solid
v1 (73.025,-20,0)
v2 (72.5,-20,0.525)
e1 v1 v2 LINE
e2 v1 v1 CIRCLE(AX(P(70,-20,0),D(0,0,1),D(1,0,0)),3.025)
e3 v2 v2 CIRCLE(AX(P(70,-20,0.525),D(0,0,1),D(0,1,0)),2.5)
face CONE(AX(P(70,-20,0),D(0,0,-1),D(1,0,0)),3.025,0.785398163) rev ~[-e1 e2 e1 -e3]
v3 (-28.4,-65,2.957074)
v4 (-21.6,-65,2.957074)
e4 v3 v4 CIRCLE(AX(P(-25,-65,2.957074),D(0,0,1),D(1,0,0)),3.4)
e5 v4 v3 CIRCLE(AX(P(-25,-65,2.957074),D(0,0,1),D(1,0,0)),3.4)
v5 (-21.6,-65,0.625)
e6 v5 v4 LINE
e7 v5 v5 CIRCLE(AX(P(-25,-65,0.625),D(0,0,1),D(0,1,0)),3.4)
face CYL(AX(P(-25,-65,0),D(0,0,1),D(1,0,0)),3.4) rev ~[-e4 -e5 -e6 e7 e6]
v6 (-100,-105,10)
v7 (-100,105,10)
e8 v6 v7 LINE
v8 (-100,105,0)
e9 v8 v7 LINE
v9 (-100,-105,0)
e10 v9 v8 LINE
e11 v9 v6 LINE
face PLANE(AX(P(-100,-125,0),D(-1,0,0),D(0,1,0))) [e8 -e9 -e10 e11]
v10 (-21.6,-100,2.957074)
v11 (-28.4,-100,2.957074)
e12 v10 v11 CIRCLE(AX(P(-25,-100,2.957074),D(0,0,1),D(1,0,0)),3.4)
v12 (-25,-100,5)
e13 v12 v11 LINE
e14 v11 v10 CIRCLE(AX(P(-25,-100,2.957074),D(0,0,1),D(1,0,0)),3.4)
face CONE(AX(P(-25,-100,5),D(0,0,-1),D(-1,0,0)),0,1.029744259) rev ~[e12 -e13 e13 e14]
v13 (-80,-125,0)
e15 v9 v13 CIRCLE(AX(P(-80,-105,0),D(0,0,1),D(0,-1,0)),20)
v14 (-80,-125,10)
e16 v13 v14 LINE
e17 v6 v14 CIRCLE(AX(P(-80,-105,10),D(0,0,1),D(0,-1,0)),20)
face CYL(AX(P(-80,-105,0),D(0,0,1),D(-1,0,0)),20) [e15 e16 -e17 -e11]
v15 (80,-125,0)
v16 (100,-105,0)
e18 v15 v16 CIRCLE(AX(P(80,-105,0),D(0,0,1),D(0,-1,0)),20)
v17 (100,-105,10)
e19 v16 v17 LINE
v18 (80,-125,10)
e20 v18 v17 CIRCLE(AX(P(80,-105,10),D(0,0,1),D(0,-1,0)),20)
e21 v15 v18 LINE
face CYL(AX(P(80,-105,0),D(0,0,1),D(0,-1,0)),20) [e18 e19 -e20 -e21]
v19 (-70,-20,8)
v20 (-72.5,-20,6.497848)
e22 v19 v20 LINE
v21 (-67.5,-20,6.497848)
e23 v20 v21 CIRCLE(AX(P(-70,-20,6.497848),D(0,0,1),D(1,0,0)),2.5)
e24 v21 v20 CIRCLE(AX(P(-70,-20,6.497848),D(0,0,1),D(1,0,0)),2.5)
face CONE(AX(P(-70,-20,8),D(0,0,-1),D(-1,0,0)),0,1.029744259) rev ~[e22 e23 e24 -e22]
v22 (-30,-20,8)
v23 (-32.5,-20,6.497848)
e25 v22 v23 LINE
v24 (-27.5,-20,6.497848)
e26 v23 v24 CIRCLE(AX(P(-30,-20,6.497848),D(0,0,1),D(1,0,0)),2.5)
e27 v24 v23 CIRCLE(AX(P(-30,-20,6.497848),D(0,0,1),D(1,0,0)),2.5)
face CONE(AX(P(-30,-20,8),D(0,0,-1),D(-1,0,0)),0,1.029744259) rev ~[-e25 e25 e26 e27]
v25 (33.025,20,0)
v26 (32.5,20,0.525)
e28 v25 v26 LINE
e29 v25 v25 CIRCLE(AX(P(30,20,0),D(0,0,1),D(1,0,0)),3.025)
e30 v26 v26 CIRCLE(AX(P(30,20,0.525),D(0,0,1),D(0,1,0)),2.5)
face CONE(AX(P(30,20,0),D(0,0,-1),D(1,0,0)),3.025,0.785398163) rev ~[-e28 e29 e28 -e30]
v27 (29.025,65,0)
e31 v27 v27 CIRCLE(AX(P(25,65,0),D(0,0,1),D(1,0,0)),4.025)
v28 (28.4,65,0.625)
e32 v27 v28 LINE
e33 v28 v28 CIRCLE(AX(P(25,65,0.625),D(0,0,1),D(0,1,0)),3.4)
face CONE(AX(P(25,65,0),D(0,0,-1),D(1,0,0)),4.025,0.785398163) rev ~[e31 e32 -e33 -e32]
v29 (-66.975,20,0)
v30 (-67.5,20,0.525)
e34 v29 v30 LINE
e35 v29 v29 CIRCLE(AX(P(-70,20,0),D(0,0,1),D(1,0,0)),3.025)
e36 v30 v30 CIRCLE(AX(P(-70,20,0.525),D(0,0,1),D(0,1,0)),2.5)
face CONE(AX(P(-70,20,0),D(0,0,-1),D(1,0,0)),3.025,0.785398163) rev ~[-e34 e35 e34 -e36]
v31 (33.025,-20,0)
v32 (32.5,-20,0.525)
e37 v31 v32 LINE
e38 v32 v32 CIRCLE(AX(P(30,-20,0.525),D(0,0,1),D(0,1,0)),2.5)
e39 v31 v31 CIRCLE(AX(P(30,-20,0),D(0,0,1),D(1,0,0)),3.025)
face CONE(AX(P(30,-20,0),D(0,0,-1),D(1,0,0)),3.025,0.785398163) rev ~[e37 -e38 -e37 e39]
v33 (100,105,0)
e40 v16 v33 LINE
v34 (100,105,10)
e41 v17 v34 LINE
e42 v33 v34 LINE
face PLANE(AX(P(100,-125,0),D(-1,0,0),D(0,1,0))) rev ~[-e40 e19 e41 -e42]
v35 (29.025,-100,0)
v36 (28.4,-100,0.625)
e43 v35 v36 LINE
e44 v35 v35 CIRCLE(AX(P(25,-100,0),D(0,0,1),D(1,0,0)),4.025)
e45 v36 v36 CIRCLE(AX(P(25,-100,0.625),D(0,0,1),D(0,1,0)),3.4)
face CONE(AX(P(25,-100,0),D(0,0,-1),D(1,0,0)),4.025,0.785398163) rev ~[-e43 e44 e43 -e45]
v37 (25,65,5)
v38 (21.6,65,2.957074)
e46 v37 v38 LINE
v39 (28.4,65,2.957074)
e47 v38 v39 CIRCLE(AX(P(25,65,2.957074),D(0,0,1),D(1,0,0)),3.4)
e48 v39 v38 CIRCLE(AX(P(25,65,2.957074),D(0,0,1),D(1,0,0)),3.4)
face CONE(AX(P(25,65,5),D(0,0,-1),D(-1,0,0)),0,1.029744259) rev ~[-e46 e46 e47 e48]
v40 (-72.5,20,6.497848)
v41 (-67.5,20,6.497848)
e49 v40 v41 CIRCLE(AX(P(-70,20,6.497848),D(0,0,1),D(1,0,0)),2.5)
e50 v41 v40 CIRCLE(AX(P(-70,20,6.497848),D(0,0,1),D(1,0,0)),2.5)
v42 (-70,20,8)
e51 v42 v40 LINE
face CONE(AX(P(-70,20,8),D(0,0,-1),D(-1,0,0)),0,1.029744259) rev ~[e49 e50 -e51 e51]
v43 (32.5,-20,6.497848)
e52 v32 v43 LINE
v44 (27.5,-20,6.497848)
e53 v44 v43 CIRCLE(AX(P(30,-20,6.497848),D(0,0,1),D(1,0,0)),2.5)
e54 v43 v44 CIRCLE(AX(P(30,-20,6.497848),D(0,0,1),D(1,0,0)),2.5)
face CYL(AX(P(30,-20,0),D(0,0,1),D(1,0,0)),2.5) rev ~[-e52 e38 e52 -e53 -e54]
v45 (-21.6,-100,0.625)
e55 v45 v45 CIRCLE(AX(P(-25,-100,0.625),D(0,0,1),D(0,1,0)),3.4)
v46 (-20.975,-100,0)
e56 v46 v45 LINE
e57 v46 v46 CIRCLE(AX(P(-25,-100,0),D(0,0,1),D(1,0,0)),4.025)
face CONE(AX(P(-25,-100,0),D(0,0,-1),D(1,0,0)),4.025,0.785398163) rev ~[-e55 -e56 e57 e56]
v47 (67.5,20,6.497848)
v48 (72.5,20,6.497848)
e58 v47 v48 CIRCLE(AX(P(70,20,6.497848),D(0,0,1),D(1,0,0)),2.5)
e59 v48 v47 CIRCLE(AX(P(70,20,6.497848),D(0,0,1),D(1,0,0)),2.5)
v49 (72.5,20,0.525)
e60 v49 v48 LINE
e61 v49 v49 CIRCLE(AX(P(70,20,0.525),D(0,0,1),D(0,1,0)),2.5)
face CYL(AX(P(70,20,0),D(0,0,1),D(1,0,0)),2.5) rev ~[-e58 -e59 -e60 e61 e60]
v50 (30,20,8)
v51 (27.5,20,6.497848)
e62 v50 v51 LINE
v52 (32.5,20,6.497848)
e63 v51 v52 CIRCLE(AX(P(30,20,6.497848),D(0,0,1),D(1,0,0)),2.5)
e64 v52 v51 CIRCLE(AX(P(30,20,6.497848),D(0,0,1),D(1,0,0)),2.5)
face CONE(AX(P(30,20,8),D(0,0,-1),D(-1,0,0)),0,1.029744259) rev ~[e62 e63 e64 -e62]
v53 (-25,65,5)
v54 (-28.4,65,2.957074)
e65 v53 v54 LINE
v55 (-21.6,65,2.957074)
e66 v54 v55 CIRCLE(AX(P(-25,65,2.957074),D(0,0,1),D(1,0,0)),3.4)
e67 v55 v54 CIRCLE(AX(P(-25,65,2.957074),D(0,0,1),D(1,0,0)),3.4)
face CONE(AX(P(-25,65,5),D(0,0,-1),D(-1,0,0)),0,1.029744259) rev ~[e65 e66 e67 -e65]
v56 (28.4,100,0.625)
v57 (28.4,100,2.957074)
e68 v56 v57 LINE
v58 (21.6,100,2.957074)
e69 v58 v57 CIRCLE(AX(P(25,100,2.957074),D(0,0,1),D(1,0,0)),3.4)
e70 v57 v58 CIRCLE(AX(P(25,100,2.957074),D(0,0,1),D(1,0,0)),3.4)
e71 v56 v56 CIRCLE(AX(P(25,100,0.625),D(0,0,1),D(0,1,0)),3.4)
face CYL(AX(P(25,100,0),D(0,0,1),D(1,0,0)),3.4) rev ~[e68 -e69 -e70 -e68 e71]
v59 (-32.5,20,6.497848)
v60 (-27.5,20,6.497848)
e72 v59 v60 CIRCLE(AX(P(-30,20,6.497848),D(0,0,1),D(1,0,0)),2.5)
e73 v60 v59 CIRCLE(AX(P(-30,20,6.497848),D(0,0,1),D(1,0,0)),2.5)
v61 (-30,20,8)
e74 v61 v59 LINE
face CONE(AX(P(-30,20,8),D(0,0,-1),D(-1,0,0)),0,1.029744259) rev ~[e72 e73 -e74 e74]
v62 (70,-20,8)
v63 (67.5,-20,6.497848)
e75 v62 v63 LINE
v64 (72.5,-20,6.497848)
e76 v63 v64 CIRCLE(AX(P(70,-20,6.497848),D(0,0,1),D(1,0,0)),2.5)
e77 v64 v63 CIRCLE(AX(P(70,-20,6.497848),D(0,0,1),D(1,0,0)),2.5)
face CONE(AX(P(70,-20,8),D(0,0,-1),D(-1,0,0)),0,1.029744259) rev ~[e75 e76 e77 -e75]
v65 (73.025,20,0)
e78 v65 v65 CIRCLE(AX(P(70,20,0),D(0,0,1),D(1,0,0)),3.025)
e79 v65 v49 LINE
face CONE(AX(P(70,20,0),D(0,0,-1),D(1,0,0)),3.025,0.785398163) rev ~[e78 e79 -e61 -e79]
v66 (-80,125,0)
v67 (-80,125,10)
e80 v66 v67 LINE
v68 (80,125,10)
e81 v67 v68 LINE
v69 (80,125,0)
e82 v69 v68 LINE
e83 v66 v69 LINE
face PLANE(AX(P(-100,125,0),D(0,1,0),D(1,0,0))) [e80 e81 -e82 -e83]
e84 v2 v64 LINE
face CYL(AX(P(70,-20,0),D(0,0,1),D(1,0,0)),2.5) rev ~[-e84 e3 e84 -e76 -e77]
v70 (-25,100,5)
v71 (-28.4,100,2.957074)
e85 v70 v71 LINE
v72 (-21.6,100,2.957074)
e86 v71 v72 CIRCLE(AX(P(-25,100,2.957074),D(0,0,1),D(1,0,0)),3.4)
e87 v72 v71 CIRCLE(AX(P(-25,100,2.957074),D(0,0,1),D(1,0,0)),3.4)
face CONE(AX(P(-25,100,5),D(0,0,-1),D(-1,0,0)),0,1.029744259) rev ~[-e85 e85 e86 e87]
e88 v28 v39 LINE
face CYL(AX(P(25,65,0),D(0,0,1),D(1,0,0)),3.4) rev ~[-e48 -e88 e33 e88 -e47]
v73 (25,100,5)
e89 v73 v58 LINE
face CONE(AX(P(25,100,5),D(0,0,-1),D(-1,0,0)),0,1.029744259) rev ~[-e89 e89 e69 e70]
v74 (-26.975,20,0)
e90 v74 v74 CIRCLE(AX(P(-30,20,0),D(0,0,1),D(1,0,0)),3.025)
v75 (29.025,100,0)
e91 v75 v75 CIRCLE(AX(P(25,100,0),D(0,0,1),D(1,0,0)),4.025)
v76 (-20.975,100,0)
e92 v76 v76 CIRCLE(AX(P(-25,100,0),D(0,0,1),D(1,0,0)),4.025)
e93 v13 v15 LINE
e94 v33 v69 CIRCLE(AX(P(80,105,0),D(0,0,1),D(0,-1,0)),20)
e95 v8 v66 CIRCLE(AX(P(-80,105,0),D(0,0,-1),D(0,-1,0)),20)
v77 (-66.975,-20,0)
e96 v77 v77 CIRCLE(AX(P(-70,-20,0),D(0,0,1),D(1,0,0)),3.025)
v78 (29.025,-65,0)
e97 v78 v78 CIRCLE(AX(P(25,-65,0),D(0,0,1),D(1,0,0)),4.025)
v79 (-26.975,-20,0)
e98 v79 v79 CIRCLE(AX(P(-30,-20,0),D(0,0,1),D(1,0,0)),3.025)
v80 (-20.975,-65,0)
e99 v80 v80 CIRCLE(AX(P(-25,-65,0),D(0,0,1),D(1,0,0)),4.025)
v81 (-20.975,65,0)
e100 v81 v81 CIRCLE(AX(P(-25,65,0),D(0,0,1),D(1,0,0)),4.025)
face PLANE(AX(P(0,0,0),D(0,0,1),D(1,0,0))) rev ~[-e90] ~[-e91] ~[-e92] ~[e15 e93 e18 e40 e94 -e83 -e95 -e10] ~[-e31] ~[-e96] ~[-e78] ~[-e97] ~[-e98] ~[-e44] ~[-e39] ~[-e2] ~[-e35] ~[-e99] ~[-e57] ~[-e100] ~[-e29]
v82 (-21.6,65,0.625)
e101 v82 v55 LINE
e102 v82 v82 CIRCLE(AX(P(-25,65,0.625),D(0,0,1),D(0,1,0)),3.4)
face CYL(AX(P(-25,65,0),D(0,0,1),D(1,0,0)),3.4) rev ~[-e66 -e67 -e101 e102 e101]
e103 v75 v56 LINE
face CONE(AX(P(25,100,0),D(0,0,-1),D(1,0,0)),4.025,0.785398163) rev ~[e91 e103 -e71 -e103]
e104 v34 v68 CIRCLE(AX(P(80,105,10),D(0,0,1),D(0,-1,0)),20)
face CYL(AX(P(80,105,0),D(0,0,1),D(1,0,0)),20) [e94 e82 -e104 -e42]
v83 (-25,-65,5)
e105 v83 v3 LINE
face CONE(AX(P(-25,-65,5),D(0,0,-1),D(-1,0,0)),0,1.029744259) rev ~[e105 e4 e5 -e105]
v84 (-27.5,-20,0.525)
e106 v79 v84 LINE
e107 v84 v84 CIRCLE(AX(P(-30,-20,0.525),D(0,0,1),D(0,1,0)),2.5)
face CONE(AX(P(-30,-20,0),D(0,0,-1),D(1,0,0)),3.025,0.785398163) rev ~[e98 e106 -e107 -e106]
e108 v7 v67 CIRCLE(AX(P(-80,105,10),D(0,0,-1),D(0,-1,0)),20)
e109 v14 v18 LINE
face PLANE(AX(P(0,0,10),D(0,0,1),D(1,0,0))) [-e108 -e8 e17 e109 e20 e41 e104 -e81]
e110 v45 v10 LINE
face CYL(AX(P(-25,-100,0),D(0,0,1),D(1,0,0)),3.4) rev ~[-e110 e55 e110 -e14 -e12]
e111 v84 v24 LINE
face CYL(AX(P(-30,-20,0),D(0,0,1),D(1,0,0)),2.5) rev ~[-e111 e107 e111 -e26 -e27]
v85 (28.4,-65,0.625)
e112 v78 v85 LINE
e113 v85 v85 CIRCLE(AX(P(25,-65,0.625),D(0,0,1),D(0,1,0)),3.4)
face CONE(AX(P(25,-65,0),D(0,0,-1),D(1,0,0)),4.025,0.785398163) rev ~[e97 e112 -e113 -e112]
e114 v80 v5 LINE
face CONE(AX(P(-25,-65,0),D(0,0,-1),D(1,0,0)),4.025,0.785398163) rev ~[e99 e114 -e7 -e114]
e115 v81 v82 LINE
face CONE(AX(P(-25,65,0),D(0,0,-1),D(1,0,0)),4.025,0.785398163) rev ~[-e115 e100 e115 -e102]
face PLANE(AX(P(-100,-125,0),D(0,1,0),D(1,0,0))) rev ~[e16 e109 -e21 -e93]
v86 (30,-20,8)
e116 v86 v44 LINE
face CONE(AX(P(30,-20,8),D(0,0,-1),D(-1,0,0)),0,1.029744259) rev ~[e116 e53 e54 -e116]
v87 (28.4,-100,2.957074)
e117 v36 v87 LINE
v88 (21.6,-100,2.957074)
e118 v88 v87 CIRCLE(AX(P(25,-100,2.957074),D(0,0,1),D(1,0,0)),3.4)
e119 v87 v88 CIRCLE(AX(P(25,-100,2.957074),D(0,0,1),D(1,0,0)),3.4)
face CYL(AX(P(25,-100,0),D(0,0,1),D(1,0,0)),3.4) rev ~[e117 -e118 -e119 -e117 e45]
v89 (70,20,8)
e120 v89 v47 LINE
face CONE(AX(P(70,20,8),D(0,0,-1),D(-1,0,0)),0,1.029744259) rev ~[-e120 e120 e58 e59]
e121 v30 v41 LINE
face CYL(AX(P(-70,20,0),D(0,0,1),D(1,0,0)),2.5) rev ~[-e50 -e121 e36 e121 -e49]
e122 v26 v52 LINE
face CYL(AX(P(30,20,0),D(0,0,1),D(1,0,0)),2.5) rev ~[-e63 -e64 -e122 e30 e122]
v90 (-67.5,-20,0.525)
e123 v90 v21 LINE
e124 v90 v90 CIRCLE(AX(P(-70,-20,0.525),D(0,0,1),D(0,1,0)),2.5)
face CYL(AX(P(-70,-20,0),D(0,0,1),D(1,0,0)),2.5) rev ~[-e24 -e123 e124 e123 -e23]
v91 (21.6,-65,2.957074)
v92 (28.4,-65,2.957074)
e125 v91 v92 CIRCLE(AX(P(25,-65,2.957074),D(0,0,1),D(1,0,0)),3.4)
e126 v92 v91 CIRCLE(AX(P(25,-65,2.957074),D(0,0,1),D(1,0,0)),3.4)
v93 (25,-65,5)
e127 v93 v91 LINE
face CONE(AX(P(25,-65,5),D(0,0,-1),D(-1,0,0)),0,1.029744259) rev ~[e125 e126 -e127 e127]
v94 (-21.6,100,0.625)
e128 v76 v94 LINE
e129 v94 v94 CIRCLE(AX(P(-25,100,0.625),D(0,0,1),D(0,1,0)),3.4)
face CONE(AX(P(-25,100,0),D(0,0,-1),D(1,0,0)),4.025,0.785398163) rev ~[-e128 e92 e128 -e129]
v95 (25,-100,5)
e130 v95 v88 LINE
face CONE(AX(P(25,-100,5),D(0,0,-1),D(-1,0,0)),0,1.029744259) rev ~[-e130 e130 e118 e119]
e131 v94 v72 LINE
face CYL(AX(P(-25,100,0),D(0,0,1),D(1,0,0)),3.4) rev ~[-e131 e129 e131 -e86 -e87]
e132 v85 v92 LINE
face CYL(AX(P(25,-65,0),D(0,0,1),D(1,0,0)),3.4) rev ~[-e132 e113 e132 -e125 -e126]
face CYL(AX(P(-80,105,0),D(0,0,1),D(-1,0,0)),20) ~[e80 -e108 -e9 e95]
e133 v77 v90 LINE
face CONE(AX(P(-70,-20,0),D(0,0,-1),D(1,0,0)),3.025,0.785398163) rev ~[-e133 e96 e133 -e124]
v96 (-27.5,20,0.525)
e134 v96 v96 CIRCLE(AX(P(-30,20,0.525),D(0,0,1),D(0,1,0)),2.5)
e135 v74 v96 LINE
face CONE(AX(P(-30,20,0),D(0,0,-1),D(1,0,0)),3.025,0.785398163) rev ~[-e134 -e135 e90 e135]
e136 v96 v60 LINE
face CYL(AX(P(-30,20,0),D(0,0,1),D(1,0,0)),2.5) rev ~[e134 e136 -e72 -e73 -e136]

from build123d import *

# Parameters (mm, degrees)
SKETCH_1_W                   = 200
SKETCH_1_H                   = 250
EXTRUDE_1_DEPTH              = 10
FILLET_1_R                   = 20
HOLE_WIZARD_M8_2_D           = 6.8
HOLE_WIZARD_M8_2_DEPTH       = 2.957073895
HOLE_WIZARD_M8_2_CSINK_D     = 8.05
HOLE_WIZARD_M8_2_CSINK_ANGLE = 90
HOLE_WIZARD_M8_2_TIP         = 2.042926105
HOLE_WIZARD_M6_1_D           = 5
HOLE_WIZARD_M6_1_DEPTH       = 6.497848452
HOLE_WIZARD_M6_1_CSINK_D     = 6.05
HOLE_WIZARD_M6_1_CSINK_ANGLE = 90
HOLE_WIZARD_M6_1_TIP         = 1.502151548


with BuildPart() as part:
    # 草图1 → 凸台-拉伸1 (new body)
    with BuildSketch(Plane.XY):
        Rectangle(SKETCH_1_W, SKETCH_1_H)
    extrude(amount=EXTRUDE_1_DEPTH)

    # 圆角1
    fillet_1_edges = [part.edges().sort_by_distance(p)[0] for p in [
        (-100, 125, 5),
        (100, 125, 5),
        (100, -125, 5),
        (-100, -125, 5),
    ]]
    fillet(fillet_1_edges, radius=FILLET_1_R)

    # M8 螺纹孔2
    with Locations(Plane(origin=(0, 0, 0), x_dir=(-1, 0, 0), z_dir=(0, 0, -1))):
        with Locations((25, -100), (25, -65), (-25, -65), (-25, -100), (25, 100), (25, 65), (-25, 65), (-25, 100)):
            CounterSinkHole(HOLE_WIZARD_M8_2_D / 2, HOLE_WIZARD_M8_2_CSINK_D / 2, depth=HOLE_WIZARD_M8_2_DEPTH, counter_sink_angle=HOLE_WIZARD_M8_2_CSINK_ANGLE)
            with Locations((0, 0, -(HOLE_WIZARD_M8_2_DEPTH + HOLE_WIZARD_M8_2_TIP / 2))):  # 118° drill point
                Cone(0, HOLE_WIZARD_M8_2_D / 2, HOLE_WIZARD_M8_2_TIP, mode=Mode.SUBTRACT)

    # M6 螺纹孔1
    with Locations(Plane(origin=(0, 0, 0), x_dir=(-1, 0, 0), z_dir=(0, 0, -1))):
        with Locations((70, 20), (30, 20), (70, -20), (30, -20), (-30, 20), (-30, -20), (-70, 20), (-70, -20)):
            CounterSinkHole(HOLE_WIZARD_M6_1_D / 2, HOLE_WIZARD_M6_1_CSINK_D / 2, depth=HOLE_WIZARD_M6_1_DEPTH, counter_sink_angle=HOLE_WIZARD_M6_1_CSINK_ANGLE)
            with Locations((0, 0, -(HOLE_WIZARD_M6_1_DEPTH + HOLE_WIZARD_M6_1_TIP / 2))):  # 118° drill point
                Cone(0, HOLE_WIZARD_M6_1_D / 2, HOLE_WIZARD_M6_1_TIP, mode=Mode.SUBTRACT)


solid = part.part
